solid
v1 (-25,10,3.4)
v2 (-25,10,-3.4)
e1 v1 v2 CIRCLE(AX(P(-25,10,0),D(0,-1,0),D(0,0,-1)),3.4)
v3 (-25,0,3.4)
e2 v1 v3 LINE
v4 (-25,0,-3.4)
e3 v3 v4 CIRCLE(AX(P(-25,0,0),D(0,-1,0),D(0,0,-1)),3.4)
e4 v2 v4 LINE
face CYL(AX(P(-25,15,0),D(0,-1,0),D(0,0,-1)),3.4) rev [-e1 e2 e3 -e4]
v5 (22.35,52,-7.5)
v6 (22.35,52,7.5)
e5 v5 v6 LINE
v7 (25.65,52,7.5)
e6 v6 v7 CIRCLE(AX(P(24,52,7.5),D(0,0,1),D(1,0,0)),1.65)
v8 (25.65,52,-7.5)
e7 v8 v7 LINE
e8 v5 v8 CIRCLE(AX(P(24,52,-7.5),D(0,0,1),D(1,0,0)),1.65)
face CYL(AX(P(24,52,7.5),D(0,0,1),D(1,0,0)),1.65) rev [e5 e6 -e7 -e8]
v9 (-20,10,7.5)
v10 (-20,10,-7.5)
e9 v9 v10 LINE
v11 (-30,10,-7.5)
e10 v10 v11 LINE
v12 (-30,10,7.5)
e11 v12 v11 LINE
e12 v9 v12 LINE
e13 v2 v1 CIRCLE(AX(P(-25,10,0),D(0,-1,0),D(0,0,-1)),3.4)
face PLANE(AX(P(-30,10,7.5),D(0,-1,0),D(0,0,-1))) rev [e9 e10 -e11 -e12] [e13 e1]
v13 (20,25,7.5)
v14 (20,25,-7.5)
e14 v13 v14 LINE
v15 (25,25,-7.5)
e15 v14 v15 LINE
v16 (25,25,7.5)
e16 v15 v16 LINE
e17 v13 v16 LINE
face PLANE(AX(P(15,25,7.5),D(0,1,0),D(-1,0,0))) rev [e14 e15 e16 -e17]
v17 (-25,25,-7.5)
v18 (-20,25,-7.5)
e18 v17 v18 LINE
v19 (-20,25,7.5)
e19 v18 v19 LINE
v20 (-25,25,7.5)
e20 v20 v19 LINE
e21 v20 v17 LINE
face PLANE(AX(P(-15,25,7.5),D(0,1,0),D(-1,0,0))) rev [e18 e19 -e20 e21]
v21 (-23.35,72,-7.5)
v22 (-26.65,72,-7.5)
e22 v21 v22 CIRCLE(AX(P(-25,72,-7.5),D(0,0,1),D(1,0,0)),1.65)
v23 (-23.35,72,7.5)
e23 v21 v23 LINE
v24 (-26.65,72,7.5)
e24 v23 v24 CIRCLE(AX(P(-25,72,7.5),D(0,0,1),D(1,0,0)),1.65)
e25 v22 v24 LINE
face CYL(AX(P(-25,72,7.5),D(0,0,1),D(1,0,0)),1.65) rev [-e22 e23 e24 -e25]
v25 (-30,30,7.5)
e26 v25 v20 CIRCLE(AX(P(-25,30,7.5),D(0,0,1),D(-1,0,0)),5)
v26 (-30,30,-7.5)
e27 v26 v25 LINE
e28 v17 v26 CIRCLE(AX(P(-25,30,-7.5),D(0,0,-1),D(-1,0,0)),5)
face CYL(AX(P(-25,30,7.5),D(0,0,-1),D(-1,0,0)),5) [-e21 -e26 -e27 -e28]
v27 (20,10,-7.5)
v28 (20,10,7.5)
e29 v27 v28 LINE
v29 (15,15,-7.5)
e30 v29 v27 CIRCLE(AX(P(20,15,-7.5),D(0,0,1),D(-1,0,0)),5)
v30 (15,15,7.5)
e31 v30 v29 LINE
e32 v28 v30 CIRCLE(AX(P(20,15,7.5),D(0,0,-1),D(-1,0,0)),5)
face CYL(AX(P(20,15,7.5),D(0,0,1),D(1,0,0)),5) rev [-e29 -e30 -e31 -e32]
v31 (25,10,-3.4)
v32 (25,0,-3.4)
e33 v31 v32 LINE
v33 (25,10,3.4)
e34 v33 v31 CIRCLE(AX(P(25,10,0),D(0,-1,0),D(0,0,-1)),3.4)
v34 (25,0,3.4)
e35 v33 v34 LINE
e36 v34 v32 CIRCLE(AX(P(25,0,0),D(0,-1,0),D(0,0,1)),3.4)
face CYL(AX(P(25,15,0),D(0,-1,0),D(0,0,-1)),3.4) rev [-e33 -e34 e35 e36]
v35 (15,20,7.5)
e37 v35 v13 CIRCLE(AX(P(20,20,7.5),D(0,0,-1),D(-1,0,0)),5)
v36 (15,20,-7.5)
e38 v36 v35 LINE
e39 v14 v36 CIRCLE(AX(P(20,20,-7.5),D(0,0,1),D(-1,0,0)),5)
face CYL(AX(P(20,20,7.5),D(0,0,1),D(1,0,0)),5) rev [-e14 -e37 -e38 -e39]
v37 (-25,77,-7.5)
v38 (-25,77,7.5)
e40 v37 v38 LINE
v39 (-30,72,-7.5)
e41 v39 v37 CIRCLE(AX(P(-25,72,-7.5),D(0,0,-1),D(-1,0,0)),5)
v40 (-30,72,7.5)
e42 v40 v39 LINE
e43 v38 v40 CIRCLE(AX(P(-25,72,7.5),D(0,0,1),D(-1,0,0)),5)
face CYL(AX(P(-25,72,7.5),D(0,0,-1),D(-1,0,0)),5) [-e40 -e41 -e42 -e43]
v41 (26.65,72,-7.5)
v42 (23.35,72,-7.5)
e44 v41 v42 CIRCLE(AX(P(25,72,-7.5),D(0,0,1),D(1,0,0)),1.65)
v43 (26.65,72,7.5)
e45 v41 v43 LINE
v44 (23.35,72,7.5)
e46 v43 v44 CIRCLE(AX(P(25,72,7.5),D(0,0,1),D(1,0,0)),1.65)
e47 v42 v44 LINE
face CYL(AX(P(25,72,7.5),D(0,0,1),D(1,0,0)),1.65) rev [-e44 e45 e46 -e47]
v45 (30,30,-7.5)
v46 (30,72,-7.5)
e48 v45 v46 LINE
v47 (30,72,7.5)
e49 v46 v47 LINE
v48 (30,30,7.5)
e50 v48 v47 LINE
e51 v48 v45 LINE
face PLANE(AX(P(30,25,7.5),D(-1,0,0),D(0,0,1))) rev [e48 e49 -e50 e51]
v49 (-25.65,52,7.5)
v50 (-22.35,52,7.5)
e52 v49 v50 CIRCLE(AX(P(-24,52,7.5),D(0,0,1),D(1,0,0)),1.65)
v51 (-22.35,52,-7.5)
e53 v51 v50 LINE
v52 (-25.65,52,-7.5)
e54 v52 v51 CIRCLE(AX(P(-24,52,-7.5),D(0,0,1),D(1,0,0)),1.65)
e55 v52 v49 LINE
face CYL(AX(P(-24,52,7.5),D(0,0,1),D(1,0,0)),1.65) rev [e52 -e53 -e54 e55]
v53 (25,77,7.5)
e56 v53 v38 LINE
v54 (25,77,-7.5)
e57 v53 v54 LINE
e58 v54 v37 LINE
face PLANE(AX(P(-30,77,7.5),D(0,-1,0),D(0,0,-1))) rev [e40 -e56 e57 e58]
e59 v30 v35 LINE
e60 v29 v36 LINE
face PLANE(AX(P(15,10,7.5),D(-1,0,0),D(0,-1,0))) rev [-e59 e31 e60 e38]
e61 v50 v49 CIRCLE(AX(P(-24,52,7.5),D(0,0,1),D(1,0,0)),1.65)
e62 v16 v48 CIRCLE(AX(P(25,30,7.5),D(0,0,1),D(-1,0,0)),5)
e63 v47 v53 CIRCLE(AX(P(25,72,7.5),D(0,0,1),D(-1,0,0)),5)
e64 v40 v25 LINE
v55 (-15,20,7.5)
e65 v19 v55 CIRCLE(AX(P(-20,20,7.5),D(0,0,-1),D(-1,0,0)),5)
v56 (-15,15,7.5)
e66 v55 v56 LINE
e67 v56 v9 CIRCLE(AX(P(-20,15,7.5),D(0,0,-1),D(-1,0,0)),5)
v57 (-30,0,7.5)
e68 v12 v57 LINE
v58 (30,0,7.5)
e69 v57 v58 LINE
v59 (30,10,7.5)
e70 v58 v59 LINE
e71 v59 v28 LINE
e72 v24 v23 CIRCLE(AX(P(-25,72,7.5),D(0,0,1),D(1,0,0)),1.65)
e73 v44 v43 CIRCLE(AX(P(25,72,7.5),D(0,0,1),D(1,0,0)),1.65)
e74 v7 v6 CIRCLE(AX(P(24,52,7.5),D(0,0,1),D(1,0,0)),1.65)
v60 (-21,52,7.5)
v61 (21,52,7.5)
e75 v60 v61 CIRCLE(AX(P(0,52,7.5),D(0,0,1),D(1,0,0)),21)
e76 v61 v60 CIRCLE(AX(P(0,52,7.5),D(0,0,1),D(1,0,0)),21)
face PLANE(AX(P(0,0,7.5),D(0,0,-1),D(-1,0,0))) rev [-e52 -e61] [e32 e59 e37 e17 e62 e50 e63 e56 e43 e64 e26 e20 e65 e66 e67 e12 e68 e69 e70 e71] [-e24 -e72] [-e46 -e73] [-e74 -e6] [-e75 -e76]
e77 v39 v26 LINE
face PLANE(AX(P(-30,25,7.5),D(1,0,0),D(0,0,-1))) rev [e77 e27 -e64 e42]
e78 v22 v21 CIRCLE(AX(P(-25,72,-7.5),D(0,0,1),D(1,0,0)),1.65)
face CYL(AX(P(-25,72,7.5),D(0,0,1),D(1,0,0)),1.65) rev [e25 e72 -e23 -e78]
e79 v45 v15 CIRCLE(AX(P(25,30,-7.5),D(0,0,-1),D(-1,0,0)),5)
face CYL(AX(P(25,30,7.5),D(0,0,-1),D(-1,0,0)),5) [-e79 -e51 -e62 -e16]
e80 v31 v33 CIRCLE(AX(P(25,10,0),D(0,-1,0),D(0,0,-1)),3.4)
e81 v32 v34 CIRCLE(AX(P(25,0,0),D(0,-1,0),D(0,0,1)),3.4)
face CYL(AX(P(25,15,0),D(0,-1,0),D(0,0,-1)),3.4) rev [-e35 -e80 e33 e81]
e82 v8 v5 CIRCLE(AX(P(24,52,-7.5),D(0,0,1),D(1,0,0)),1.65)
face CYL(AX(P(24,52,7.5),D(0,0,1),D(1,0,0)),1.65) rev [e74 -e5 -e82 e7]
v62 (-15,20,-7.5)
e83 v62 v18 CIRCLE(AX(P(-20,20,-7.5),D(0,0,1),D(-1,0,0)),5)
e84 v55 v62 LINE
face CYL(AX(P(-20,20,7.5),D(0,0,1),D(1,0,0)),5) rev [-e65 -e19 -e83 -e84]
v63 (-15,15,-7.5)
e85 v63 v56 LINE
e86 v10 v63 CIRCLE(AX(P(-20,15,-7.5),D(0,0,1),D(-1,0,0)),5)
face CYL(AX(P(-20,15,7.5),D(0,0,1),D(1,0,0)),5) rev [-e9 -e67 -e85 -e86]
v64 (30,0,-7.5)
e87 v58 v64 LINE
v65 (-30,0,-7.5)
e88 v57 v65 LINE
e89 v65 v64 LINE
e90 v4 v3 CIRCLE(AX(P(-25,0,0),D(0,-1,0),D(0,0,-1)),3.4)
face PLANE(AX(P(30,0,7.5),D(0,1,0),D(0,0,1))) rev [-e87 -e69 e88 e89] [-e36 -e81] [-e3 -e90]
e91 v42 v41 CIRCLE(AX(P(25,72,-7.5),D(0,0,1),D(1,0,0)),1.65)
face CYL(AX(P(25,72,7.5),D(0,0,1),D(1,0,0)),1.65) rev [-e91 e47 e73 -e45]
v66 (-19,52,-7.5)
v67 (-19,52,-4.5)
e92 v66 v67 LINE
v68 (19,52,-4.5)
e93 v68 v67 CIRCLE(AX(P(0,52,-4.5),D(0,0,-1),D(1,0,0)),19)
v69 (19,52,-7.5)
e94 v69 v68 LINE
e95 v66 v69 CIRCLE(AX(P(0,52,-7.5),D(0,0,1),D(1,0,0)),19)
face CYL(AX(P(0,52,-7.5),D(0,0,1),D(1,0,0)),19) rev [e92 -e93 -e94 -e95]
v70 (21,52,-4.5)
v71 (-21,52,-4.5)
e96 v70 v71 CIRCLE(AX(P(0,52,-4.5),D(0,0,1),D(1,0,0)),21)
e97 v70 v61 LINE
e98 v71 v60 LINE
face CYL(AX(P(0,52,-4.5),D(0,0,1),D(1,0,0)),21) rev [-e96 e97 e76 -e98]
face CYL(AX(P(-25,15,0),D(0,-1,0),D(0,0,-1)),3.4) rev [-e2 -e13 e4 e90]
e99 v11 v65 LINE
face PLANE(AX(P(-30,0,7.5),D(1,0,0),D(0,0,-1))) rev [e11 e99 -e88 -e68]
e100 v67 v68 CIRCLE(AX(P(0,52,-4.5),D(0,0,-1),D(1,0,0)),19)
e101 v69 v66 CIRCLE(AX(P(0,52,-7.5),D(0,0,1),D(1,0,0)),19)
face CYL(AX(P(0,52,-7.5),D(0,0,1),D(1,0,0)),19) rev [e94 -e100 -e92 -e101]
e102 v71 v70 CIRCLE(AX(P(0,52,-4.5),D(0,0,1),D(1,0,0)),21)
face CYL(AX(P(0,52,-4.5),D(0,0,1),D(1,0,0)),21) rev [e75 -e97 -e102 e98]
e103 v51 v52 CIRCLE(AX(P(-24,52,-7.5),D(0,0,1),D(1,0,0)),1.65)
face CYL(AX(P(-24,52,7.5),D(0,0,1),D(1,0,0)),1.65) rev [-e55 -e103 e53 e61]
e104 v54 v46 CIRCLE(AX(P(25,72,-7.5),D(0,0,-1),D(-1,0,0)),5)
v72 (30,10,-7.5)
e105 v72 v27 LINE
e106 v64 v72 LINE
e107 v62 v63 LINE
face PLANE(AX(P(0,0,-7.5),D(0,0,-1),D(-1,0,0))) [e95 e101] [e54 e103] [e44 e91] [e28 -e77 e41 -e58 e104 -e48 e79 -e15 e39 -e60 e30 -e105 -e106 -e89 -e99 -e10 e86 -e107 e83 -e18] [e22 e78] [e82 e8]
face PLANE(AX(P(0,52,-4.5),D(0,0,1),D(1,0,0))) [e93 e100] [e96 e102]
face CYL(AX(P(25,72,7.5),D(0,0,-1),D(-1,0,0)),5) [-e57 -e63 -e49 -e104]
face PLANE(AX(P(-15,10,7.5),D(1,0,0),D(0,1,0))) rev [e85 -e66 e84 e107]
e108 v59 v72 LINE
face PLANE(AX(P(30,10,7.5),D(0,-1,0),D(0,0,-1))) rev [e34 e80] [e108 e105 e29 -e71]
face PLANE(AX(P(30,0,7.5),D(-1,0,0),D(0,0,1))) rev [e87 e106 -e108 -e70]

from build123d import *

# Parameters (mm, degrees)
BOSS_EXTRUDE1_DEPTH = 7.5
SKETCH2_R           = 3.4
CUT_EXTRUDE1_DEPTH  = 15
SKETCH4_R           = 19
CUT_EXTRUDE3_DEPTH  = 84.988094394
SKETCH3_R           = 21
CUT_EXTRUDE4_DEPTH  = 12
M4_TAPPED_HOLE2_D   = 3.3
M4_TAPPED_HOLE1_D   = 3.3
FILLET2_R           = 5


with BuildPart() as part:
    # Sketch1 → Boss-Extrude1 (new, symmetric)
    with BuildSketch(Plane.XY):
        Polygon((30, 0), (-30, 0), (-30, 10), (-15, 10), (-15, 25), (-30, 25), (-30, 77), (30, 77), (30, 25), (15, 25), (15, 10), (30, 10), align=None)
    extrude(amount=BOSS_EXTRUDE1_DEPTH, both=True)

    # Sketch2 → Cut-Extrude1 (cut)
    with BuildSketch(Plane.XZ):
        with Locations(Location((-25, 0, 0), (0, 0, 270))):
            Circle(SKETCH2_R)
        with Locations(Location((25, 0, 0), (0, 0, 270))):
            Circle(SKETCH2_R)
    extrude(amount=-CUT_EXTRUDE1_DEPTH, mode=Mode.SUBTRACT)

    # Sketch4 → Cut-Extrude3 (cut, through all)
    with BuildSketch(Plane.XY.offset(7.5)):
        with Locations((0, 52)):
            Circle(SKETCH4_R)
    extrude(amount=-CUT_EXTRUDE3_DEPTH, mode=Mode.SUBTRACT)

    # Sketch3 → Cut-Extrude4 (cut)
    with BuildSketch(Plane.XY.offset(7.5)):
        with Locations((0, 52)):
            Circle(SKETCH3_R)
    extrude(amount=-CUT_EXTRUDE4_DEPTH, mode=Mode.SUBTRACT)

    # M4 Tapped Hole2 (through all)
    with Locations(Plane.XY.offset(7.5)):
        with Locations((24, 52), (-24, 52)):
            Hole(M4_TAPPED_HOLE2_D / 2)

    # M4 Tapped Hole1 (through all)
    with Locations(Plane.XY.offset(7.5)):
        with Locations((-25, 72), (25, 72)):
            Hole(M4_TAPPED_HOLE1_D / 2)

    # Fillet2
    fillet2_edges = [part.edges().sort_by_distance(p)[0] for p in [
        (-30, 25, 0),
        (-30, 77, 0),
        (30, 77, 0),
        (30, 25, 0),
        (15, 25, 0),
        (15, 10, 0),
        (-15, 10, 0),
        (-15, 25, 0),
    ]]
    fillet(fillet2_edges, radius=FILLET2_R)


solid = part.part
